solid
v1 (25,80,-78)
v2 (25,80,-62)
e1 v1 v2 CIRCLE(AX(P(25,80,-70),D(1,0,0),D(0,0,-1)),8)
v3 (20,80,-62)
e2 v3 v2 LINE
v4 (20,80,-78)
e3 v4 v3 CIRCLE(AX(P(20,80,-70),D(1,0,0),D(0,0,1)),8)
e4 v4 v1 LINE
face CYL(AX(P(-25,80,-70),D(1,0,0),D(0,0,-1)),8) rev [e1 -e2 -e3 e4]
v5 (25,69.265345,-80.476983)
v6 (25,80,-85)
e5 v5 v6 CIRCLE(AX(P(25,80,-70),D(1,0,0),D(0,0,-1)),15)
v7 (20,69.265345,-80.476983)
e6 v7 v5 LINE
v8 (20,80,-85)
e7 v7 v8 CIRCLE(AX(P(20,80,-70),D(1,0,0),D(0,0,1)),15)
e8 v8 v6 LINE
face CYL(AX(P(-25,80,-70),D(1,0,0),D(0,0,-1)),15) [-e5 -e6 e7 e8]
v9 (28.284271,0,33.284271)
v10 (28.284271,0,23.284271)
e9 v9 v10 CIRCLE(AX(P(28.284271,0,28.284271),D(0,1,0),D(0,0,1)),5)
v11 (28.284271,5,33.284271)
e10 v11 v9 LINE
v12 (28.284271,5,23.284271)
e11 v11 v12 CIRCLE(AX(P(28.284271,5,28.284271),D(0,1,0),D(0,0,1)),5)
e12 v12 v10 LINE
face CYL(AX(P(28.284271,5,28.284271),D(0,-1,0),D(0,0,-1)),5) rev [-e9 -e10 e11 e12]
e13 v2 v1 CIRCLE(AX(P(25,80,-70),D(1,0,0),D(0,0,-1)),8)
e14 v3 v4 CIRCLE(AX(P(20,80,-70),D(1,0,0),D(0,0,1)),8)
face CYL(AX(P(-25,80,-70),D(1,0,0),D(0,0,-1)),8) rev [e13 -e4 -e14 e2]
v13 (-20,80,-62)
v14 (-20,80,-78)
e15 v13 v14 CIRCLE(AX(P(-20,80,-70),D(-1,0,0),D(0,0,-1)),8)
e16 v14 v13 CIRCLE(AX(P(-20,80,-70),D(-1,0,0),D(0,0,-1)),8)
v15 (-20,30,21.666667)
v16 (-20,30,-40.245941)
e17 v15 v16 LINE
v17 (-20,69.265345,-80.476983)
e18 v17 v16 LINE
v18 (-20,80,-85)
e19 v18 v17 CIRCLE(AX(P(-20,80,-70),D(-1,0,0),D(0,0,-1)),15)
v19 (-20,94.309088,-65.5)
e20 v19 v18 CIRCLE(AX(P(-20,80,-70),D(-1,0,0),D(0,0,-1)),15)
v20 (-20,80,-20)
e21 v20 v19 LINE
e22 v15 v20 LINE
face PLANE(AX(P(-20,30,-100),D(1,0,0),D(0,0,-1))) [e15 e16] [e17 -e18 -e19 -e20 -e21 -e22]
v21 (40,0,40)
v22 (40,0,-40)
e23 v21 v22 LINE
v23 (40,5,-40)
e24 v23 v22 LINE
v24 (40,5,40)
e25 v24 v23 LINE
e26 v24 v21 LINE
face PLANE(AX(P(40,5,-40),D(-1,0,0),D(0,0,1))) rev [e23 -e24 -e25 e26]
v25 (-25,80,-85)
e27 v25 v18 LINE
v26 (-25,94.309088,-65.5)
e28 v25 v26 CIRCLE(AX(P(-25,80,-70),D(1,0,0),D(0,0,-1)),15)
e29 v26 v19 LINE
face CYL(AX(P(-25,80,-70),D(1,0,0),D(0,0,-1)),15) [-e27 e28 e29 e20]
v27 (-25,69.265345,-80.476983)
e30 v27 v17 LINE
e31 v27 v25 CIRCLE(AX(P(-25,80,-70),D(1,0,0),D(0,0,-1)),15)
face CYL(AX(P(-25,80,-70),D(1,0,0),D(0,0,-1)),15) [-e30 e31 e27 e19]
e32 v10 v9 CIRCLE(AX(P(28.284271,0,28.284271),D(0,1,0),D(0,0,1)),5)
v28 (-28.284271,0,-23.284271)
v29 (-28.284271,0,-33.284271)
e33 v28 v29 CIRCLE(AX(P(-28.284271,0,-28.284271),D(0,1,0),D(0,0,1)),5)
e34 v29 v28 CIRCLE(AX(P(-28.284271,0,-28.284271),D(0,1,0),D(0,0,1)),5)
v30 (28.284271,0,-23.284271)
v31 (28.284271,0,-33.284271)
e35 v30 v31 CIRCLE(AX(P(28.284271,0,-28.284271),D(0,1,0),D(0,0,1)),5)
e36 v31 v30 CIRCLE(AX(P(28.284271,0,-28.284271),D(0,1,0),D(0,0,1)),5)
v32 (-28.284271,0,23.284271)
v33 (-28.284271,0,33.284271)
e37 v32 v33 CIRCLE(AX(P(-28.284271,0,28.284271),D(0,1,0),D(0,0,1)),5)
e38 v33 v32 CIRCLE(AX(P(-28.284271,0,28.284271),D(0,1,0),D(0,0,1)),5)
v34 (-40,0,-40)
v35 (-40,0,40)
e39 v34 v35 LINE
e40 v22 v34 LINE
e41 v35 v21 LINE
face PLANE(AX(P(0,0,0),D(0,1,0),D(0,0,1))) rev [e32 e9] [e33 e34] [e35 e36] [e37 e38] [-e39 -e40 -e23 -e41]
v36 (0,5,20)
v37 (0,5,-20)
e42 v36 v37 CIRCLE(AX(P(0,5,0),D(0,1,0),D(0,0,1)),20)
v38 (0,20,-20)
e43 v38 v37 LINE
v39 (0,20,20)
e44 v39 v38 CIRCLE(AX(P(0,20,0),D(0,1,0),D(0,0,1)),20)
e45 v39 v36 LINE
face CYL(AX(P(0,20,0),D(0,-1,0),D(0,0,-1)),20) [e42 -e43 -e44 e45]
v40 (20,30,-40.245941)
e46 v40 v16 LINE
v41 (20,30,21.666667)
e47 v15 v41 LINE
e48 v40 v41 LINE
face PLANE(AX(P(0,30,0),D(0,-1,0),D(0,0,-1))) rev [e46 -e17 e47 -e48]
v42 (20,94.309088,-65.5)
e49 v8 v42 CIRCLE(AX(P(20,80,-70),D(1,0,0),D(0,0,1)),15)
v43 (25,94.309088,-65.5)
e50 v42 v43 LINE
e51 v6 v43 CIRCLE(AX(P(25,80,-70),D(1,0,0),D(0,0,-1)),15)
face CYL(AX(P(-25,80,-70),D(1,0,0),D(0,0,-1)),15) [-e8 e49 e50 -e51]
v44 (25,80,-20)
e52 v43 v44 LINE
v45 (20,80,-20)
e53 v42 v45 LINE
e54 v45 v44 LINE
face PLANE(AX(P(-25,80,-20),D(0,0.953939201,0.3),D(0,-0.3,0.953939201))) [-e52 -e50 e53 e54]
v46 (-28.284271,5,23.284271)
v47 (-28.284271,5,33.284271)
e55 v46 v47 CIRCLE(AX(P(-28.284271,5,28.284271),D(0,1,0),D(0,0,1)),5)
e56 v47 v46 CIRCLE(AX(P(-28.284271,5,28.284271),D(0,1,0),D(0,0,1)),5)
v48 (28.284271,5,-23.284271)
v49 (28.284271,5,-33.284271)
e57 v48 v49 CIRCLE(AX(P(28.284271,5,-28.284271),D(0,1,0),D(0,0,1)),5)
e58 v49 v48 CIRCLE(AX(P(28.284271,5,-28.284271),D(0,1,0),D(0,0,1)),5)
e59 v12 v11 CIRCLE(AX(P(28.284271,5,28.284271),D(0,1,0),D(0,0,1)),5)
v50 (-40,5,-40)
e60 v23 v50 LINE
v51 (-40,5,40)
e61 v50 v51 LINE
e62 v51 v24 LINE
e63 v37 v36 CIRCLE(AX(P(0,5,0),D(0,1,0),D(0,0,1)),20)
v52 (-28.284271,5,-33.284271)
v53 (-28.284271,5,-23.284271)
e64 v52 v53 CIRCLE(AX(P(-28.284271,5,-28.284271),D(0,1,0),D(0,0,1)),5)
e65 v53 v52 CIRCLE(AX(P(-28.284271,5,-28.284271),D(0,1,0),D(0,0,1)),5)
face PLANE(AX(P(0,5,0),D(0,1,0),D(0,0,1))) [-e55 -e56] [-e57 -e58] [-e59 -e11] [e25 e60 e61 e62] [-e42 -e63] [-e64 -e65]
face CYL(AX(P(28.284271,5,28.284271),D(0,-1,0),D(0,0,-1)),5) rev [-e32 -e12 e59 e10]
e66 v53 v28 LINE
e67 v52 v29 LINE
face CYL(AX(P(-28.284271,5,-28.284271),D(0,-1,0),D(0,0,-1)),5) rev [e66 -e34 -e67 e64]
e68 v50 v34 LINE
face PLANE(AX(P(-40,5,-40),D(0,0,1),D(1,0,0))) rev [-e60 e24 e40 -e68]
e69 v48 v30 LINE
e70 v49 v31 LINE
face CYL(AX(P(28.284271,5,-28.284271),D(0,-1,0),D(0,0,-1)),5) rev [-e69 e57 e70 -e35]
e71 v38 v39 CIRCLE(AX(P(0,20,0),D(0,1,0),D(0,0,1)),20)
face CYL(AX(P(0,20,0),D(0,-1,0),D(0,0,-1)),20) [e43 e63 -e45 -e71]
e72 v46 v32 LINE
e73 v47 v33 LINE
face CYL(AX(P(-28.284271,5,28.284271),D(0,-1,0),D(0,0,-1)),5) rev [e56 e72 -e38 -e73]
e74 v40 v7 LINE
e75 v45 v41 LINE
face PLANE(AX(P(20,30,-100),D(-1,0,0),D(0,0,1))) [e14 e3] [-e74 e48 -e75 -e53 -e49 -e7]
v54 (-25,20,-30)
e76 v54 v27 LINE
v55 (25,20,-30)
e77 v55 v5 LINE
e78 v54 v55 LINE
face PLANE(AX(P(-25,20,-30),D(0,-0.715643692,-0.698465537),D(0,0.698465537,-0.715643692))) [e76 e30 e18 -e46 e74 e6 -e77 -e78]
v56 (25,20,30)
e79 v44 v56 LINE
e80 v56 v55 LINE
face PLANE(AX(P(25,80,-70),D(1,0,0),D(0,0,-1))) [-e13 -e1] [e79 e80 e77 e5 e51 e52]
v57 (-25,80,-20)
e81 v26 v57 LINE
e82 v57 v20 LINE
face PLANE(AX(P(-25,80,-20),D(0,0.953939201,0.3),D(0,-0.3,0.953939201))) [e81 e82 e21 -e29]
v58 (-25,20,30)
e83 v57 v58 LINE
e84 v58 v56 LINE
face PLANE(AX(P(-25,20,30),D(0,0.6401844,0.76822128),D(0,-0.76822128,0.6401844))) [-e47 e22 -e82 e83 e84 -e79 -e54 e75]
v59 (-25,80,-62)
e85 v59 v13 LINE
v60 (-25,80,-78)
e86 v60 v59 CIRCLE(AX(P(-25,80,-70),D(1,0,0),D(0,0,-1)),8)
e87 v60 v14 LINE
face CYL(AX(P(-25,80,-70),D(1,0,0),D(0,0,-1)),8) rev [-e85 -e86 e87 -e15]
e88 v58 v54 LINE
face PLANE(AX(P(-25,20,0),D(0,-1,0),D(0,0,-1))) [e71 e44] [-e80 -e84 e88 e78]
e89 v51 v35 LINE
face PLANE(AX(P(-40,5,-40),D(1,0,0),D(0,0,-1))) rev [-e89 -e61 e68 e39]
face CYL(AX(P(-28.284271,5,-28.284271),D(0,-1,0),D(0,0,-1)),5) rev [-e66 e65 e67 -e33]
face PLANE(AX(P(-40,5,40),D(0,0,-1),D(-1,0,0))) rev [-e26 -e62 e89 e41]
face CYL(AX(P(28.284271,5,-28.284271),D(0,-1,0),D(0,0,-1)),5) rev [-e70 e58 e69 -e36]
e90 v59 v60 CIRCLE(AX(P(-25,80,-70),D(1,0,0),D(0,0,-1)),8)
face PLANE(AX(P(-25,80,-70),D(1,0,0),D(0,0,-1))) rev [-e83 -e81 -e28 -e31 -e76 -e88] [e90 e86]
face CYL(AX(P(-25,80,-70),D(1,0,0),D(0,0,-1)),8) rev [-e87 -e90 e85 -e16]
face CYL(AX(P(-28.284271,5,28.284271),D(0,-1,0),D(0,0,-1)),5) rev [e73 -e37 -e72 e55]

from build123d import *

# Parameters (mm, degrees)
SKETCH1_W                = 80
SKETCH1_H                = 80
SKETCH1_R                = 5
BOSS_EXTRUDE3_DEPTH      = 5
SKETCH3_R                = 20
BOSS_EXTRUDE4_DEPTH      = 15
BOSS_EXTRUDE6_DEPTH      = 25
BOSS_EXTRUDE6_DEPTH_BACK = 25
SKETCH6_R                = 8
CUT_EXTRUDE1_DEPTH       = 50
CUT_EXTRUDE1_DEPTH_BACK  = 25
SKETCH8_W                = 40
SKETCH8_H                = 200


with BuildPart() as part:
    # Sketch1 → Boss-Extrude3 (new body)
    with BuildSketch(Plane(origin=(0, 0, 0), x_dir=(1, 0, 0), z_dir=(0, 1, 0))):
        Rectangle(SKETCH1_W, SKETCH1_H)
        with Locations(Location((-28.284271247, -28.284271247, 0), (0, 0, 270))):
            Circle(SKETCH1_R, mode=Mode.SUBTRACT)
        with Locations(Location((-28.284271247, 28.284271247, 0), (0, 0, 270))):
            Circle(SKETCH1_R, mode=Mode.SUBTRACT)
        with Locations(Location((28.284271247, 28.284271247, 0), (0, 0, 270))):
            Circle(SKETCH1_R, mode=Mode.SUBTRACT)
        with Locations(Location((28.284271247, -28.284271247, 0), (0, 0, 270))):
            Circle(SKETCH1_R, mode=Mode.SUBTRACT)
    extrude(amount=BOSS_EXTRUDE3_DEPTH)

    # Sketch3 → Boss-Extrude4 (add)
    with BuildSketch(Plane(origin=(0, 5, 0), x_dir=(1, 0, 0), z_dir=(0, 1, 0))):
        with Locations(Location((0, 0, 0), (0, 0, 270))):
            Circle(SKETCH3_R)
    extrude(amount=BOSS_EXTRUDE4_DEPTH)

    # Sketch6 → Boss-Extrude6 (add, two sides: drawn at the far end of the back side and taken through both)
    with BuildSketch(Plane(origin=(0, 0, 0), x_dir=(0, 0, -1), z_dir=(1, 0, 0)).offset(-BOSS_EXTRUDE6_DEPTH_BACK)):
        with BuildLine():
            Line((0, 20), (30, 20))
            Line((30, 20), (80.476983059, 69.265344627))
            ThreePointArc((80.476983059, 69.265344627), (82.87355244, 87.698808192), (65.5, 94.309088021))
            Line((65.5, 94.309088021), (20, 80))
            Line((20, 80), (-30, 20))
            Line((-30, 20), (0, 20))
        make_face()
        with Locations((70, 80)):
            Circle(SKETCH6_R, mode=Mode.SUBTRACT)
    extrude(amount=BOSS_EXTRUDE6_DEPTH + BOSS_EXTRUDE6_DEPTH_BACK)

    # Sketch8 → Cut-Extrude1 (cut, two sides: drawn at the far end of the back side and taken through both)
    with BuildSketch(Plane(origin=(0, 80, 0), x_dir=(-1, 0, 0), z_dir=(0, -1, 0)).offset(-CUT_EXTRUDE1_DEPTH_BACK)):
        Rectangle(SKETCH8_W, SKETCH8_H)
    extrude(amount=CUT_EXTRUDE1_DEPTH + CUT_EXTRUDE1_DEPTH_BACK, mode=Mode.SUBTRACT)


solid = part.part
